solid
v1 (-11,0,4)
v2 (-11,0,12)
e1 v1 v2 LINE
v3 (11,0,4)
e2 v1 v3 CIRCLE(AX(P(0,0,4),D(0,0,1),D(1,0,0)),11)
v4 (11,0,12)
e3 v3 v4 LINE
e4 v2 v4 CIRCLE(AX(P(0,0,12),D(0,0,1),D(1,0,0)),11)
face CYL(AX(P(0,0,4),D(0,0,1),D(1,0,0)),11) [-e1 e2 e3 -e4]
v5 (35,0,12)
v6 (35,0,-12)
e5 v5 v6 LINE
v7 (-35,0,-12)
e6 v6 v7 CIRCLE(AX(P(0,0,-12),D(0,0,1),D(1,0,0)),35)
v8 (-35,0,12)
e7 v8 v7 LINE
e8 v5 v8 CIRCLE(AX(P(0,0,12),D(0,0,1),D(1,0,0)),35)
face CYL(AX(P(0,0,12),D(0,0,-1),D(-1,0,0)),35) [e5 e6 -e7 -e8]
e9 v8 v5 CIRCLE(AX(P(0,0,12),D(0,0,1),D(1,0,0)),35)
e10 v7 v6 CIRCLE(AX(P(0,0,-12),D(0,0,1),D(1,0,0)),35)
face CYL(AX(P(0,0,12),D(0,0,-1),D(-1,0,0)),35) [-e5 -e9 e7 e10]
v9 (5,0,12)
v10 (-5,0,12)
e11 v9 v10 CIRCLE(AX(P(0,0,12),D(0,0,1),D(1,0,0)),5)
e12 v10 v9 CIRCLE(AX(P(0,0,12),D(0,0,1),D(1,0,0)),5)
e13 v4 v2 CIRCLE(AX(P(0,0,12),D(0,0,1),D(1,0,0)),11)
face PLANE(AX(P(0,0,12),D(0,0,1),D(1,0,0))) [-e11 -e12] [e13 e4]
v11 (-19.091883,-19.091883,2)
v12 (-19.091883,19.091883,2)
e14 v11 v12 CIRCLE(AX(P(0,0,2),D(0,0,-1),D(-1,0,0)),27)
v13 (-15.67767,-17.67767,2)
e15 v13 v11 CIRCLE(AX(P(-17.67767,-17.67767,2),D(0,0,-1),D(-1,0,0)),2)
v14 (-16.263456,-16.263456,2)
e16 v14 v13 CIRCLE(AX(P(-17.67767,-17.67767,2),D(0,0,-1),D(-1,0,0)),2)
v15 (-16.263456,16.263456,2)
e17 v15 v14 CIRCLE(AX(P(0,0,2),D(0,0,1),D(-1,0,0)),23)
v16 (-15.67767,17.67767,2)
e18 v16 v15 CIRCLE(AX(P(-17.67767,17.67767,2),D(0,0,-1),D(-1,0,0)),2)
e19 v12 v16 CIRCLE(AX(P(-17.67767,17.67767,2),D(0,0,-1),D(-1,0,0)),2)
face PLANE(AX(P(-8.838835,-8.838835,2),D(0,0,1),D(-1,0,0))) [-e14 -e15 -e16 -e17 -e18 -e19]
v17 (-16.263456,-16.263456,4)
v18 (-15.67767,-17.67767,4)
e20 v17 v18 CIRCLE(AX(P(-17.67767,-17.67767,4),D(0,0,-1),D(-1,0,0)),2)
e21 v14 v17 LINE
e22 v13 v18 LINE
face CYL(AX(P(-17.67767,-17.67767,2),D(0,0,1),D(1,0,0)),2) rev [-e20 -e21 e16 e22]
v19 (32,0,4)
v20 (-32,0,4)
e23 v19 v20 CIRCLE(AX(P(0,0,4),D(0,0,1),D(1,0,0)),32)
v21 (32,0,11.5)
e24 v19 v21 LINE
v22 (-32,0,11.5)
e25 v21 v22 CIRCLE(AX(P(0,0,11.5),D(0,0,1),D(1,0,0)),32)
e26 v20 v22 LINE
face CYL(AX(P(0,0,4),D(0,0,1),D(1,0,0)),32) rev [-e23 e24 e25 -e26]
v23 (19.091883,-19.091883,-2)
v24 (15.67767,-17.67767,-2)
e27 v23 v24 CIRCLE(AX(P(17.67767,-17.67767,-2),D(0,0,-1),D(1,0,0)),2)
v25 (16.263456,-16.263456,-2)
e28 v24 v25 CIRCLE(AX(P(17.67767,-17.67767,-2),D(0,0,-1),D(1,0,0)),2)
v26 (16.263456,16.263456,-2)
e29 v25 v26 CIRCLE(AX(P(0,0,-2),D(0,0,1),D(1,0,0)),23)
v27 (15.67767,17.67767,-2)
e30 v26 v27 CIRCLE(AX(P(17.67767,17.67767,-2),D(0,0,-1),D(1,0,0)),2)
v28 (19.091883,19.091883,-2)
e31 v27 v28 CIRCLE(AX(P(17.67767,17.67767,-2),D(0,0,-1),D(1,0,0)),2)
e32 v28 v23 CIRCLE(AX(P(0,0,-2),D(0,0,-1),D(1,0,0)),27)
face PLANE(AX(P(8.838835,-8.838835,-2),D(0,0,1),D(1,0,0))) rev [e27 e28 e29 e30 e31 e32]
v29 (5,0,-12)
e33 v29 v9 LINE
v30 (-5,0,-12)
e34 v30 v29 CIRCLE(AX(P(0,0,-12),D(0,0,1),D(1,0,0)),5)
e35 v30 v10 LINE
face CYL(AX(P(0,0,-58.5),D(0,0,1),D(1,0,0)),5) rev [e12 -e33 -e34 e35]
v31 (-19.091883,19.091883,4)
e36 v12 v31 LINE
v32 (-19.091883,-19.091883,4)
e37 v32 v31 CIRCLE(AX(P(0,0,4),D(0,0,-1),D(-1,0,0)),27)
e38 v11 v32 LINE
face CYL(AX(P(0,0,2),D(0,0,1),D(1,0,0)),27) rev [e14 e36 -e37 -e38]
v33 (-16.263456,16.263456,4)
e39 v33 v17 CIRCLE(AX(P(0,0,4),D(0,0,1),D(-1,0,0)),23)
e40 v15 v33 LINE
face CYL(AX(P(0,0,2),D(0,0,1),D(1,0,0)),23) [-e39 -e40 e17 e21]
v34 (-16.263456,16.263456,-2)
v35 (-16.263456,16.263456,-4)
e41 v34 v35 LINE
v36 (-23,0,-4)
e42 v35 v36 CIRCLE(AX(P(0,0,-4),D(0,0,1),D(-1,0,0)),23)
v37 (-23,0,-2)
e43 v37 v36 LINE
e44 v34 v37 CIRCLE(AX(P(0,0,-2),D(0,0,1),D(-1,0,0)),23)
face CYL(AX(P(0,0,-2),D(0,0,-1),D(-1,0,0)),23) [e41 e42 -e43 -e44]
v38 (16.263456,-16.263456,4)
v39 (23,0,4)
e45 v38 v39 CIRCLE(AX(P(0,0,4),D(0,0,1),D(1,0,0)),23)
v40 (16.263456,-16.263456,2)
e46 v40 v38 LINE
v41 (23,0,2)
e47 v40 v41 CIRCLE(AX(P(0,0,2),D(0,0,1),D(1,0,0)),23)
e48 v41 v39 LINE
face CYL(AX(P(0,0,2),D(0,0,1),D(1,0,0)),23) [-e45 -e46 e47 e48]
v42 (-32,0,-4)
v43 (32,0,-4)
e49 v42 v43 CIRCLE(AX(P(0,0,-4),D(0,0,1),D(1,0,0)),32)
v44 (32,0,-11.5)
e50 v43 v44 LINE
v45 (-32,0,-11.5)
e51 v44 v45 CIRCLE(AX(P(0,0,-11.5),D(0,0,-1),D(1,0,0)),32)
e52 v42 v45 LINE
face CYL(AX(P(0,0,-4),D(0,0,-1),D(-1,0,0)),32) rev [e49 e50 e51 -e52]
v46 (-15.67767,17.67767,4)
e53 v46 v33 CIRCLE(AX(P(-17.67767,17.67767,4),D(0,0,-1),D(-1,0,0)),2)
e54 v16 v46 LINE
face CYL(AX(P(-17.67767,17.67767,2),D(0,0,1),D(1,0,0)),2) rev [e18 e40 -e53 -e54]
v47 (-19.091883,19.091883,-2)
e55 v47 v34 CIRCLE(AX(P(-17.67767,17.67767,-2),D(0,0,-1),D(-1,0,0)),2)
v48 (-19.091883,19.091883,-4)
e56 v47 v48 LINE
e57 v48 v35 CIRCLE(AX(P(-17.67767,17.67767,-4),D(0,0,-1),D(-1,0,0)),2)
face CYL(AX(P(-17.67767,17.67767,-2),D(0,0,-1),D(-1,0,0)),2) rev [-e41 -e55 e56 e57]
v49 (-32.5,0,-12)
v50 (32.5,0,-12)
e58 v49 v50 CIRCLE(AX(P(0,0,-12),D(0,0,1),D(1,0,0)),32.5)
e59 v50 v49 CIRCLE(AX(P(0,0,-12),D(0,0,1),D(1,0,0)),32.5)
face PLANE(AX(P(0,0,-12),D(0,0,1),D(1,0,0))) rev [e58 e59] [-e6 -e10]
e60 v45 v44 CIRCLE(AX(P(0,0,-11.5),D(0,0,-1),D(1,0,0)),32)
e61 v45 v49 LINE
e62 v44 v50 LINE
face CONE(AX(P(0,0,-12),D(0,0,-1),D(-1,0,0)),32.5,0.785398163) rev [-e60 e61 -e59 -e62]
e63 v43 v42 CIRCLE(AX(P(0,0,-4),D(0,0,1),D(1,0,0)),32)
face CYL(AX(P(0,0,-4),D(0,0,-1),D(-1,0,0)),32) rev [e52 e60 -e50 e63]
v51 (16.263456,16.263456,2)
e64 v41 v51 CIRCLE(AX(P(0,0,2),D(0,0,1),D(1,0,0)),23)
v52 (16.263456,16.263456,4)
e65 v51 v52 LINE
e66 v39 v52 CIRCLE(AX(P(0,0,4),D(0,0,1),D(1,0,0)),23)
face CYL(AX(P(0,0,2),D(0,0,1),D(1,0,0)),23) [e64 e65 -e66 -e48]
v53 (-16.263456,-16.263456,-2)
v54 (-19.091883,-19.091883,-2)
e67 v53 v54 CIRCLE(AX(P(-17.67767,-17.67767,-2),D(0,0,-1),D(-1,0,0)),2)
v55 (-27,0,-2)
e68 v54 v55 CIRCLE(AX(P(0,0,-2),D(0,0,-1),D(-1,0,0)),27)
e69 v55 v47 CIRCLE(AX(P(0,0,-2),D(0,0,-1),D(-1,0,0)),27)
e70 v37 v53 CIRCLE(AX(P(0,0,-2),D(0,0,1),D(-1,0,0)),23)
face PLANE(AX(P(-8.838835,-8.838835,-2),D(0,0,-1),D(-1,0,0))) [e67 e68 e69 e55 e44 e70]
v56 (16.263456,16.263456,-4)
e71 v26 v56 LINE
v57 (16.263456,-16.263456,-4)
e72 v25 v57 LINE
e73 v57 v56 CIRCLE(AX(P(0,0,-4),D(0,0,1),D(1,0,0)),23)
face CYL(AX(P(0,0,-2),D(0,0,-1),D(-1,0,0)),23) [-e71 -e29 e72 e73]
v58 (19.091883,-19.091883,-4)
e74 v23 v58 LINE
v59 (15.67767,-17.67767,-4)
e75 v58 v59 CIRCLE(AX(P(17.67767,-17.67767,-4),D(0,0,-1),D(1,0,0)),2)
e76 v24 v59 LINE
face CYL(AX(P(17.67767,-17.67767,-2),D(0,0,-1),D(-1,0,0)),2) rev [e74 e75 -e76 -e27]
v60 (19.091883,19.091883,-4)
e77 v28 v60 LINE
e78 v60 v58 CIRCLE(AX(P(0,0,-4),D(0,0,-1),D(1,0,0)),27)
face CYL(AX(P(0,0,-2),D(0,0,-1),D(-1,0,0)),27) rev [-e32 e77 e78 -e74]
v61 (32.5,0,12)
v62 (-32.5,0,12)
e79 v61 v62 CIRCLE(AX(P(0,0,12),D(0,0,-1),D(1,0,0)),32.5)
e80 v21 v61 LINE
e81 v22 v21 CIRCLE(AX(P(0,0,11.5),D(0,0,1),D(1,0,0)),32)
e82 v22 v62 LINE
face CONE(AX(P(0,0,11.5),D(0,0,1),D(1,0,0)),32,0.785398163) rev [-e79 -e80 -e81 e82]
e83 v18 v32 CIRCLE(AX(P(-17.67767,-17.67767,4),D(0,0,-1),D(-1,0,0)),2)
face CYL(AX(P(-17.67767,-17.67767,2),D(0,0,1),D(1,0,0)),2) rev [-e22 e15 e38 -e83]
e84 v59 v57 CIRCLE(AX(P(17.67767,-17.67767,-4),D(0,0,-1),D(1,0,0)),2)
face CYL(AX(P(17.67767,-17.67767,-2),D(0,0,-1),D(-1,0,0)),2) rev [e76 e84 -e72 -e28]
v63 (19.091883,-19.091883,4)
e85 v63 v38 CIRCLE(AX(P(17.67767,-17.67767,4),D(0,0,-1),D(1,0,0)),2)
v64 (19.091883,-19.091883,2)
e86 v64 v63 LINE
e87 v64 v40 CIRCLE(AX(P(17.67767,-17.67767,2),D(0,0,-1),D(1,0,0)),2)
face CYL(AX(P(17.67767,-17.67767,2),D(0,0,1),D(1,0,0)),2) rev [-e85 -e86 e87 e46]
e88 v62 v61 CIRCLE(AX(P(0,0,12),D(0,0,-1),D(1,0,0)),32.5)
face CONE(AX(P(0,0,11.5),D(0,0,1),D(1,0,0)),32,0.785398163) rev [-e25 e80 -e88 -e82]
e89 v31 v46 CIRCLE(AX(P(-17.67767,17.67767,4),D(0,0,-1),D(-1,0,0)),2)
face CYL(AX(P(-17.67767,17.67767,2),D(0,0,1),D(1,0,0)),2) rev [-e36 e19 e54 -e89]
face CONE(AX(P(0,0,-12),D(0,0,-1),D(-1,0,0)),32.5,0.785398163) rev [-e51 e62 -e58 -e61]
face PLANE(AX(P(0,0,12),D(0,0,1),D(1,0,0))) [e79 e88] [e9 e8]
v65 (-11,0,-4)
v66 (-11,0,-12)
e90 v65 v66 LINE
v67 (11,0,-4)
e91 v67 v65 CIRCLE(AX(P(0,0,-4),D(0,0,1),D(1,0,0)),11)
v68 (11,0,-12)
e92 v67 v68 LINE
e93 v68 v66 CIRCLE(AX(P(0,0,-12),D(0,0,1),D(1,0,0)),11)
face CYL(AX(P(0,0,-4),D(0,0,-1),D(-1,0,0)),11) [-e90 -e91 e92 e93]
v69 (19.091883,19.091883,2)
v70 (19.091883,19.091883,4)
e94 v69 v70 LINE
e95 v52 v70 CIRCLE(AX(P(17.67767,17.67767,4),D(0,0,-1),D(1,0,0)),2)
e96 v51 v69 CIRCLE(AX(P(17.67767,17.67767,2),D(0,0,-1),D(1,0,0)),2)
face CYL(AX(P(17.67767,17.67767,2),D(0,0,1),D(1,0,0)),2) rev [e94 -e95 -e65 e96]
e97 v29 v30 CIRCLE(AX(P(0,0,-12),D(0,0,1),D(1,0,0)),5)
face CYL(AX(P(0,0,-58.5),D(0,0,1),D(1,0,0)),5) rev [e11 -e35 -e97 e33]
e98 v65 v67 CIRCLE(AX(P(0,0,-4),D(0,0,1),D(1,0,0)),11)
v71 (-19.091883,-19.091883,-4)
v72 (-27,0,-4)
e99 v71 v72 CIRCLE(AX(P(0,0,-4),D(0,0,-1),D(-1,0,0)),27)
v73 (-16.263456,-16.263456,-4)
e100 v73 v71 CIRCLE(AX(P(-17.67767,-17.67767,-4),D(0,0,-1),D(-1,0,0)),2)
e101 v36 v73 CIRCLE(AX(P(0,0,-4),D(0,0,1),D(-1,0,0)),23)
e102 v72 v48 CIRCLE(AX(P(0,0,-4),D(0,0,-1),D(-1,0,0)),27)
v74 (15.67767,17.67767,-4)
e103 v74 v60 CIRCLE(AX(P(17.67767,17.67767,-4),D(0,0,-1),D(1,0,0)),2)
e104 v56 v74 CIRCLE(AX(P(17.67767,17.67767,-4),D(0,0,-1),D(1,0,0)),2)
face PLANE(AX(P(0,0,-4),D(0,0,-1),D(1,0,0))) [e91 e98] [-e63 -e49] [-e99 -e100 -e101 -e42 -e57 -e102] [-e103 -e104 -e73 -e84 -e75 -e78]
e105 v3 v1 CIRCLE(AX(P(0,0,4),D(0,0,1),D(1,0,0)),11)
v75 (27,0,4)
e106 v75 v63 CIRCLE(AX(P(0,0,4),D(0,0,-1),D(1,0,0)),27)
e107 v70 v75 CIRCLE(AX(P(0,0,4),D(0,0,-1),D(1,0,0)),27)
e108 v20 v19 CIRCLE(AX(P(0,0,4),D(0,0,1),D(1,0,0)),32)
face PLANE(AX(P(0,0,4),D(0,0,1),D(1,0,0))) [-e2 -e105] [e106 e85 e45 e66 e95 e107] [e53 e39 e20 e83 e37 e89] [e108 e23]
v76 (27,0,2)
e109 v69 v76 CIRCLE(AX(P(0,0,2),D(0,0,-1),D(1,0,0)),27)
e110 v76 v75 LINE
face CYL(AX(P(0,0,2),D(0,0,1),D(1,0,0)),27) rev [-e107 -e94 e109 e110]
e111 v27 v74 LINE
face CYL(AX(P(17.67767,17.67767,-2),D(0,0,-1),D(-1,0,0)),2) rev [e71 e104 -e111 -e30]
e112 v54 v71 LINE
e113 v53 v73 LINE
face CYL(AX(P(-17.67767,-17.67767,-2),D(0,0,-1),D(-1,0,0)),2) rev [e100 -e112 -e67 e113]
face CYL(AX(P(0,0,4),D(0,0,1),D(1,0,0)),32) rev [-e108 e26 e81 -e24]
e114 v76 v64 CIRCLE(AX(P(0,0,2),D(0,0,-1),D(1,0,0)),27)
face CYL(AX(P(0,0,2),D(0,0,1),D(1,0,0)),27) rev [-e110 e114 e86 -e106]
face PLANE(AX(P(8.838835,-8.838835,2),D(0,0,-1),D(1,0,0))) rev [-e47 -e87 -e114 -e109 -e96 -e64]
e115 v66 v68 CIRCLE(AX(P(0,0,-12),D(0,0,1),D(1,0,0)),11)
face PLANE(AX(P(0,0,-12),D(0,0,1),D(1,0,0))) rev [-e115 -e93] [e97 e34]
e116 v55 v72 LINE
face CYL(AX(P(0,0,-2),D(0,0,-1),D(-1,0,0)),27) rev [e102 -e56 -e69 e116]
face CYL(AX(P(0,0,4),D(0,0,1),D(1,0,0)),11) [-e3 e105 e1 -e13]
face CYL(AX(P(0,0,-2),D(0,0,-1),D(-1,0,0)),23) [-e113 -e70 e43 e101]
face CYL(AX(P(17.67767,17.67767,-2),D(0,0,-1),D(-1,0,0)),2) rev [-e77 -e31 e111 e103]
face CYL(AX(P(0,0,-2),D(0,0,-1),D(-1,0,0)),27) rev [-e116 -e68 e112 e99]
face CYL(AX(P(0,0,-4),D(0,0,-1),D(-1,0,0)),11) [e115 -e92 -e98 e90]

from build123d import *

# Parameters (mm, degrees)
SKETCH1_R           = 35
BOSS_EXTRUDE1_DEPTH = 12
SKETCH2_R           = 5
CUT_EXTRUDE1_DEPTH  = 70.5
SKETCH3_R           = 32
SKETCH3_R_2         = 11
CUT_EXTRUDE2_DEPTH  = 8
CUT_EXTRUDE3_DEPTH  = 2
CHAMFER1_SIZE       = 0.5


with BuildPart() as part:
    # Sketch1 → Boss-Extrude1 (new, symmetric)
    with BuildSketch(Plane.XY):
        Circle(SKETCH1_R)
    extrude(amount=BOSS_EXTRUDE1_DEPTH, both=True)

    # Sketch2 → Cut-Extrude1 (cut, symmetric)
    with BuildSketch(Plane.XY.offset(12)):
        Circle(SKETCH2_R)
    extrude(amount=CUT_EXTRUDE1_DEPTH, both=True, mode=Mode.SUBTRACT)

    # Sketch3 → Cut-Extrude2 (cut)
    with BuildSketch(Plane.XY.offset(12)):
        Circle(SKETCH3_R)
        Circle(SKETCH3_R_2, mode=Mode.SUBTRACT)
    cut_extrude2 = extrude(amount=-CUT_EXTRUDE2_DEPTH, mode=Mode.SUBTRACT)

    # Mirror1: Cut-Extrude2 across plane
    add(cut_extrude2.mirror(Plane.XY), mode=Mode.SUBTRACT)

    # Sketch4 → Cut-Extrude3 (cut)
    with BuildSketch(Plane(origin=(0, 0, -4), x_dir=(-1, 0, 0), z_dir=(0, 0, -1))):
        with BuildLine():
            ThreePointArc((19.091883092, -19.091883092), (27, 0), (19.091883092, 19.091883092))
            ThreePointArc((19.091883092, 19.091883092), (16.263455967, 19.091883092), (16.263455967, 16.263455967))
            ThreePointArc((16.263455967, 16.263455967), (23, 0), (16.263455967, -16.263455967))
            ThreePointArc((16.263455967, -16.263455967), (16.263455967, -19.091883092), (19.091883092, -19.091883092))
        make_face()
        with BuildLine():
            ThreePointArc((-19.091883092, -19.091883092), (-27, 0), (-19.091883092, 19.091883092))
            ThreePointArc((-19.091883092, 19.091883092), (-16.263455967, 19.091883092), (-16.263455967, 16.263455967))
            ThreePointArc((-16.263455967, 16.263455967), (-23, 0), (-16.263455967, -16.263455967))
            ThreePointArc((-16.263455967, -16.263455967), (-16.263455967, -19.091883092), (-19.091883092, -19.091883092))
        make_face()
    cut_extrude3 = extrude(amount=-CUT_EXTRUDE3_DEPTH, mode=Mode.SUBTRACT)

    # Mirror2: Cut-Extrude3 across plane
    add(cut_extrude3.mirror(Plane.XY), mode=Mode.SUBTRACT)

    # Chamfer1
    chamfer1_edges = [part.edges().sort_by_distance(p)[0] for p in [
        (-32, 0, 12),
        (-32, 0, -12),
    ]]
    chamfer(chamfer1_edges, length=CHAMFER1_SIZE)


solid = part.part
